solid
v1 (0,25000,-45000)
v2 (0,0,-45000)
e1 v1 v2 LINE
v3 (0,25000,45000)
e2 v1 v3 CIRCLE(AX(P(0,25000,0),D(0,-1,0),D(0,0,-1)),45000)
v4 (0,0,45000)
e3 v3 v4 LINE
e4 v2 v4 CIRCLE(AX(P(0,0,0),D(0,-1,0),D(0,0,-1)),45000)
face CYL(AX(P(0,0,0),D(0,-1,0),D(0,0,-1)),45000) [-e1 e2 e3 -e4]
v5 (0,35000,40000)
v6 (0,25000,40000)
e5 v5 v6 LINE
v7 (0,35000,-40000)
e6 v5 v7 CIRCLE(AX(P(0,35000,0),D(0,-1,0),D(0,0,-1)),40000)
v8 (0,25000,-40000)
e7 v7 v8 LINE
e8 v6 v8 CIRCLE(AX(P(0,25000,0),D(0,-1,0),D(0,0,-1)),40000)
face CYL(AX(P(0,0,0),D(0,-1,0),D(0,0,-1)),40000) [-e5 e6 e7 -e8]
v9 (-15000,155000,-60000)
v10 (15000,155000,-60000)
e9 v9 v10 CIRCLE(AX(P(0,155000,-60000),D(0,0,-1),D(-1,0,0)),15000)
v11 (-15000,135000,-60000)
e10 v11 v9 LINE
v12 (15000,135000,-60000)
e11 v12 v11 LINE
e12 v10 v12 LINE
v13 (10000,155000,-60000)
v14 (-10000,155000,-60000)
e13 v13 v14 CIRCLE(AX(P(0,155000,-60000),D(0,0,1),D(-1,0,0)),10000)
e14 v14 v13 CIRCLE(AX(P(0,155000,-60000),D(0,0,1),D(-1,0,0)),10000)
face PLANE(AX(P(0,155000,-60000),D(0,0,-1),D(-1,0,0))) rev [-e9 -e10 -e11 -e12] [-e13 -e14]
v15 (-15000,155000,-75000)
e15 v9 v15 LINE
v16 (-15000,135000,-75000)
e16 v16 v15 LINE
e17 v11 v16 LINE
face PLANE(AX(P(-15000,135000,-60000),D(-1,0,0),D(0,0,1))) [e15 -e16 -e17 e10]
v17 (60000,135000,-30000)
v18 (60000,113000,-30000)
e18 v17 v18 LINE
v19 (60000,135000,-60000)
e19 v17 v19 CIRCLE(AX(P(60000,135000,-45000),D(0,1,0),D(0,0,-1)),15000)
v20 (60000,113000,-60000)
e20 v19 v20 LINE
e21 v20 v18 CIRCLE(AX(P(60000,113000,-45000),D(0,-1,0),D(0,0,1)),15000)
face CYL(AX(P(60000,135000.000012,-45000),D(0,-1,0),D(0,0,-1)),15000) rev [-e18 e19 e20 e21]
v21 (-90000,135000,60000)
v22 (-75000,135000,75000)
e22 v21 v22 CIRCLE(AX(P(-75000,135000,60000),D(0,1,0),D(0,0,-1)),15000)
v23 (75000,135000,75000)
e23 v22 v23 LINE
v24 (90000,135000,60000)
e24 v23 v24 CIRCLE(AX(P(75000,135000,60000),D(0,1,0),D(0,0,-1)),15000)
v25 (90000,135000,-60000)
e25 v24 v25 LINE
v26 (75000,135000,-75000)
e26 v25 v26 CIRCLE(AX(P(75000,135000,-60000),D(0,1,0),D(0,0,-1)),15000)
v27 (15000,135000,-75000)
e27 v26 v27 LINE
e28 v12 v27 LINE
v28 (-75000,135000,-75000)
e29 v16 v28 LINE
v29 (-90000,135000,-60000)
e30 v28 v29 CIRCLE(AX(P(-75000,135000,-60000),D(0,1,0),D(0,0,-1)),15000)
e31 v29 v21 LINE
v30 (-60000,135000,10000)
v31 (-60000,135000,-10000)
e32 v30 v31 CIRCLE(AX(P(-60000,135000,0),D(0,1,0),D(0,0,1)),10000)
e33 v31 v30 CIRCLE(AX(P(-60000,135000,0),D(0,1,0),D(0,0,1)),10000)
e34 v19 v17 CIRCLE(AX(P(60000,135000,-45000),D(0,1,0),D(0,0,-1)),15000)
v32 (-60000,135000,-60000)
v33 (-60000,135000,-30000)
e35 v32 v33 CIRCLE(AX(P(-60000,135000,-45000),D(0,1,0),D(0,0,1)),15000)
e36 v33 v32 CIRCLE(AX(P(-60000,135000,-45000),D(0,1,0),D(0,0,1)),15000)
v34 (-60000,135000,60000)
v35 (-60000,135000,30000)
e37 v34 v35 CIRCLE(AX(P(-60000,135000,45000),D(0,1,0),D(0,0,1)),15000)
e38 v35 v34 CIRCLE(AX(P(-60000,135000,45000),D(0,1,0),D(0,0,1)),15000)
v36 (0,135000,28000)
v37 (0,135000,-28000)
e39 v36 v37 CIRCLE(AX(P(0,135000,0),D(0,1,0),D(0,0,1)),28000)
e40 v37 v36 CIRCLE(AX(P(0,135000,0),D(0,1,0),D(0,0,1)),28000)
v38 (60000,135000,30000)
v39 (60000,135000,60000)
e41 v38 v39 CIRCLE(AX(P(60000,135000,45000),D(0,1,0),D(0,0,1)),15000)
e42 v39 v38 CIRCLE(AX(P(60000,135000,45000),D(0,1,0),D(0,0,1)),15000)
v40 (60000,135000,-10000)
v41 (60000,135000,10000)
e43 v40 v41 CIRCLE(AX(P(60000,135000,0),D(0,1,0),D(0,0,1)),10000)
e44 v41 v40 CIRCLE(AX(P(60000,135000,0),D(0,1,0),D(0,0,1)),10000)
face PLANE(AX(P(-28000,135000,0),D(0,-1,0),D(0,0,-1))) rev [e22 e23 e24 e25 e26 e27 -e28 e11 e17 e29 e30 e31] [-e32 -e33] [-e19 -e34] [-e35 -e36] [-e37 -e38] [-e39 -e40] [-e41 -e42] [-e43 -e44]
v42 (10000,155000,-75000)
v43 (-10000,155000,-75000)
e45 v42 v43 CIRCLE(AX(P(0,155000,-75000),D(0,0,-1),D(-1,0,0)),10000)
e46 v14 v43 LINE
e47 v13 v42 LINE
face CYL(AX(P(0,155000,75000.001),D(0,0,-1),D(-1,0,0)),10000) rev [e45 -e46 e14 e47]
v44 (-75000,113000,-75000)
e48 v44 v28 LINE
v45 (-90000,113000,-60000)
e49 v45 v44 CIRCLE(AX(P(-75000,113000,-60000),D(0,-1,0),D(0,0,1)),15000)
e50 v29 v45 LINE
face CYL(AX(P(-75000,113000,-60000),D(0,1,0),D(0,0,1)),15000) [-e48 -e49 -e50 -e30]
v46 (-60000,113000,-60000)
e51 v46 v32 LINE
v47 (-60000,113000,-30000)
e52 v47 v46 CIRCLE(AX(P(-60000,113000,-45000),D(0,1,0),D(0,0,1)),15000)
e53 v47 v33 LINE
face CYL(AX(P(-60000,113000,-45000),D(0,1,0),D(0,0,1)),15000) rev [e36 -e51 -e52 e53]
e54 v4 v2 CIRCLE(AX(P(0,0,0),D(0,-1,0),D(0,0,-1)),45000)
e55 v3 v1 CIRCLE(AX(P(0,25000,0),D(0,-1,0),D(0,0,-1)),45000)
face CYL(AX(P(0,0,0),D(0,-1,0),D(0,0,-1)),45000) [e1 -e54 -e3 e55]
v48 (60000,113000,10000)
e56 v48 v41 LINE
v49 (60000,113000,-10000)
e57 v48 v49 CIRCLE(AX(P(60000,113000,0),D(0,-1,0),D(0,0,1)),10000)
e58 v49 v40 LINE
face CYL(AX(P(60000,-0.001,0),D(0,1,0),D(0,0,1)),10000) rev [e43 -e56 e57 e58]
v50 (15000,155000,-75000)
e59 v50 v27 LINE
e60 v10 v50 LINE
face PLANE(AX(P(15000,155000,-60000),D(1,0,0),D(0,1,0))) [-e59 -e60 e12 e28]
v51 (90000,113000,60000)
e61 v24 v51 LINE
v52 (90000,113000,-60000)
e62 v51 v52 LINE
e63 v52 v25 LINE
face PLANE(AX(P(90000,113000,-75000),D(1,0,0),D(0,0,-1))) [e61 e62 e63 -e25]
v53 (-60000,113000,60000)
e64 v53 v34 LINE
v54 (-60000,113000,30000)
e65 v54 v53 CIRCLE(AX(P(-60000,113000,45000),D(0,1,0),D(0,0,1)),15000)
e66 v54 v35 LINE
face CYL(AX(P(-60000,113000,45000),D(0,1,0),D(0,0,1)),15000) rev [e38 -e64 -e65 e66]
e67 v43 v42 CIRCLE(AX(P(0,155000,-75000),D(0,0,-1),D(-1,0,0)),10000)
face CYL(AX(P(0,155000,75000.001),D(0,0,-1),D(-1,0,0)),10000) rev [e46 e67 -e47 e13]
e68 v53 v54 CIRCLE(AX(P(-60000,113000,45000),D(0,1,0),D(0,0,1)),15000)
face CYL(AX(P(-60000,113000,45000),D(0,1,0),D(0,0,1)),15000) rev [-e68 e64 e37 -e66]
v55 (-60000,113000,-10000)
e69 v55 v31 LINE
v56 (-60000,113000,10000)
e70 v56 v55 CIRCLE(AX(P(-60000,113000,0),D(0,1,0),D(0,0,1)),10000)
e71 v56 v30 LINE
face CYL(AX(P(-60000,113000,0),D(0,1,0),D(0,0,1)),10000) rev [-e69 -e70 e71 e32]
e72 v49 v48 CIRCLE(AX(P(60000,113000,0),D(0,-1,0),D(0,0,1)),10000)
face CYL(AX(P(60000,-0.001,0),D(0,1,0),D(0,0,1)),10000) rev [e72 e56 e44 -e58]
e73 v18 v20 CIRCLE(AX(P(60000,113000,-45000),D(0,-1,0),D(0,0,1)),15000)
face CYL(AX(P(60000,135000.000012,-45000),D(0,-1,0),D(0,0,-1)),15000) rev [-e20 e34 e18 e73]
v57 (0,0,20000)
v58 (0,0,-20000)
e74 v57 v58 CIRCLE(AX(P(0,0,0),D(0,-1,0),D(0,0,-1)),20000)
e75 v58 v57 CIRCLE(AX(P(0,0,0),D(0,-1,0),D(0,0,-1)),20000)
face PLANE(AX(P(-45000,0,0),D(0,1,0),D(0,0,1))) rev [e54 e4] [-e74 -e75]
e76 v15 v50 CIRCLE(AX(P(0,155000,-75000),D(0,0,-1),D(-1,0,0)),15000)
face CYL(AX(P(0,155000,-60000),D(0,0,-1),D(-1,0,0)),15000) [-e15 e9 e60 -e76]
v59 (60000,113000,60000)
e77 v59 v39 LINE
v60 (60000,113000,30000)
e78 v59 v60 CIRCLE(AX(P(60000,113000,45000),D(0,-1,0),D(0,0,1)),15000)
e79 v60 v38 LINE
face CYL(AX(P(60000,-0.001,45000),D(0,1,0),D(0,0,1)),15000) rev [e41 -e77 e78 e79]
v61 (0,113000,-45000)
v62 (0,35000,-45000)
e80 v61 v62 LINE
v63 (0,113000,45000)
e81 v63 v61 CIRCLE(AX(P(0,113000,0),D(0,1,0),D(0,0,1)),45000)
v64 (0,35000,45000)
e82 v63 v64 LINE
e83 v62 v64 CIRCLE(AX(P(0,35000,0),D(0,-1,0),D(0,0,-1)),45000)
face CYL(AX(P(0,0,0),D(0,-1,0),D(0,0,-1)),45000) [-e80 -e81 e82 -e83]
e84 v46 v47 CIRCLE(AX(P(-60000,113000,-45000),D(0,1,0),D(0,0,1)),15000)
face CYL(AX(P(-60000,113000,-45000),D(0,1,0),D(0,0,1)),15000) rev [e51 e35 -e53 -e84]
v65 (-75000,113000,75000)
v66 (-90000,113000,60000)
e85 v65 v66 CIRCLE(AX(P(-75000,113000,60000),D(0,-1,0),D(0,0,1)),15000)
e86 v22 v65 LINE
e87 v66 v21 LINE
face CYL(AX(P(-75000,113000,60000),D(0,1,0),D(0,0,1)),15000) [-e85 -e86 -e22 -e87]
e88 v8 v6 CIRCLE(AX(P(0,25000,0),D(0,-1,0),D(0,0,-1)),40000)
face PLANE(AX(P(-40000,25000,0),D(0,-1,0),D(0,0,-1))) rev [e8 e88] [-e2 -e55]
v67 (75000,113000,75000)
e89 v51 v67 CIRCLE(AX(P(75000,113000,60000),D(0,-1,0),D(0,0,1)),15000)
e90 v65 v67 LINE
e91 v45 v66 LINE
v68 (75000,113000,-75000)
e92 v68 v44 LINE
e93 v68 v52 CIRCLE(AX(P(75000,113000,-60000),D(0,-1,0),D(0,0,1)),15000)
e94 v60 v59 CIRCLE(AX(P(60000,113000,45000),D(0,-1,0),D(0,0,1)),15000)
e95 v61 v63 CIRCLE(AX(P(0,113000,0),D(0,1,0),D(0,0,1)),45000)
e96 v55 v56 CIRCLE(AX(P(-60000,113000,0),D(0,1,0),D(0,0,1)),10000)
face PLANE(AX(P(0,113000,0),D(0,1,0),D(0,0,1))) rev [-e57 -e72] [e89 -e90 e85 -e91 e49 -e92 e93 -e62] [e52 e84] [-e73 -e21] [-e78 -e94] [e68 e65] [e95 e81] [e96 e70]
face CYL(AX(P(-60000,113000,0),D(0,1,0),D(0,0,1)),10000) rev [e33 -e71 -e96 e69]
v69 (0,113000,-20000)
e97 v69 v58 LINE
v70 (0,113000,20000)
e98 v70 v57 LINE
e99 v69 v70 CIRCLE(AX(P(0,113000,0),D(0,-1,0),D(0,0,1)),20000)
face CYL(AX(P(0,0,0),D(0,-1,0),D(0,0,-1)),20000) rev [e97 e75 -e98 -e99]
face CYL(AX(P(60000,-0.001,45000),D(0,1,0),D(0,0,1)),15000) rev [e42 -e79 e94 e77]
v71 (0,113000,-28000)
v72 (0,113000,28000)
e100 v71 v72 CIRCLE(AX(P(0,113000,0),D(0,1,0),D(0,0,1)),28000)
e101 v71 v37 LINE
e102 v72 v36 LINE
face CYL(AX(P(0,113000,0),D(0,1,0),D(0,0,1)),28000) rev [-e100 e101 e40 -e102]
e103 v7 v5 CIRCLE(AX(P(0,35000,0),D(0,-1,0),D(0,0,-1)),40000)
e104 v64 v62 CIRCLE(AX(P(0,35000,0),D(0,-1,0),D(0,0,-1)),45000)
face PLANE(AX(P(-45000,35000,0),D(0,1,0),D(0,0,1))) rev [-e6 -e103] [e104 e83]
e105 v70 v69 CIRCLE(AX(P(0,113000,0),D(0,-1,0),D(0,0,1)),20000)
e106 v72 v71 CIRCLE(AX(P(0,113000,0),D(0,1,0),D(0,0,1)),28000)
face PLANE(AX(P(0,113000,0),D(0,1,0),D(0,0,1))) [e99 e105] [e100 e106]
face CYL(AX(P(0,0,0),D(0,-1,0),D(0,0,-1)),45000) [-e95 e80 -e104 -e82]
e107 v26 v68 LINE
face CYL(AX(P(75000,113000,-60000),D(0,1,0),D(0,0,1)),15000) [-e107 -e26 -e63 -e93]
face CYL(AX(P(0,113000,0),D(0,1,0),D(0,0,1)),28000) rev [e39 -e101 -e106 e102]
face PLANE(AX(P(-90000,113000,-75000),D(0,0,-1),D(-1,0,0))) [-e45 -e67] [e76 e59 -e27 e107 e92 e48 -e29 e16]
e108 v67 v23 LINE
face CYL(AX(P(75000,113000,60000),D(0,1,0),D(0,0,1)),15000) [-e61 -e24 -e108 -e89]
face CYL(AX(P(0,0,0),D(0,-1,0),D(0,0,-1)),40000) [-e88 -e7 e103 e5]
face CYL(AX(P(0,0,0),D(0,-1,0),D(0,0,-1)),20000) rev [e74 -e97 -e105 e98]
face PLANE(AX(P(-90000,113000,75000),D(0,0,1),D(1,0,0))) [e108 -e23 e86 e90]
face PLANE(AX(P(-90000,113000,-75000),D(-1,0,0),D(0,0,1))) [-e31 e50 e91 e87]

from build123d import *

# Parameters (mm, degrees)
FLANGE_PROFILE_180X150_W         = 180000
FLANGE_PROFILE_180X150_H         = 150000
SQUARE_FLANGE_DEPTH              = 22000
CENTRE_RECESS_SKETCH_R           = 28000
CENTRE_RECESS_DEPTH              = 22000
FLANGE_CORNER_FILLET_R15_A_R     = 15000
FLANGE_CORNER_FILLET_R15_B_R     = 15000
FLANGE_CORNER_FILLET_R15_C_R     = 15000
FLANGE_CORNER_FILLET_R15_D_R     = 15000
BOLT_HOLE_30_A_SKETCH_R          = 15000
BOLT_HOLE_30_A_DEPTH             = 22000
PIN_HOLE_20_A_SKETCH_R           = 10000
PIN_HOLE_20_A_DEPTH              = 22000
BOLT_HOLE_30_B_SKETCH_R          = 15000
BOLT_HOLE_30_B_DEPTH             = 22000
BOLT_HOLE_30_C_REACH             = 178747.629
BOLT_HOLE_30_C_SKETCH_R          = 15000
BOLT_HOLE_30_C_DIRECTION_2_DEPTH = 178746.629317195
PIN_HOLE_20_B_REACH              = 178747.629
PIN_HOLE_20_B_SKETCH_R           = 10000
BOLT_HOLE_30_D_REACH             = 178747.629
BOLT_HOLE_30_D_SKETCH_R          = 15000
LIFTING_LUG_DEPTH                = 15000
LIFTING_EYE_HOLE_REACH           = 243928.218
LIFTING_EYE_HOLE_SKETCH_R        = 10000


with BuildPart() as part:
    # Plug Body Profile → Plug Body (revolve)
    with BuildSketch(Plane.XY, mode=Mode.PRIVATE) as plug_body_sk:
        Polygon((-20000, 0), (-20000, 121000), (-28000, 121000), (-28000, 135000), (-53000, 135000), (-53000, 115000), (-45000, 115000), (-45000, 35000), (-40000, 35000), (-40000, 25000), (-45000, 25000), (-45000, 0), align=None)
    revolve(plug_body_sk.sketch.rotate(Axis((0, 0, 0), (0, 1, 0)), 270), axis=Axis((0, 0, 0), (0, 1, 0)))

    # Flange Profile 180x150 → Square Flange (add)
    with BuildSketch(Plane(origin=(0, 135000, 0), x_dir=(1, 0, 0), z_dir=(0, 1, 0))):
        Rectangle(FLANGE_PROFILE_180X150_W, FLANGE_PROFILE_180X150_H)
    extrude(amount=-SQUARE_FLANGE_DEPTH)

    # Centre Recess Sketch → Centre Recess (cut)
    with BuildSketch(Plane(origin=(0, 135000, 0), x_dir=(1, 0, 0), z_dir=(0, 1, 0))):
        with Locations(Location((0, 0, 0), (0, 0, 270))):
            Circle(CENTRE_RECESS_SKETCH_R)
    extrude(amount=-CENTRE_RECESS_DEPTH, mode=Mode.SUBTRACT)

    # Flange Corner Fillet R15 A
    flange_corner_fillet_r15_a_edges = [part.edges().sort_by_distance(p)[0] for p in [
        (90000, 124000, 75000),
    ]]
    fillet(flange_corner_fillet_r15_a_edges, radius=FLANGE_CORNER_FILLET_R15_A_R)

    # Flange Corner Fillet R15 B
    flange_corner_fillet_r15_b_edges = [part.edges().sort_by_distance(p)[0] for p in [
        (-90000, 124000, 75000),
    ]]
    fillet(flange_corner_fillet_r15_b_edges, radius=FLANGE_CORNER_FILLET_R15_B_R)

    # Flange Corner Fillet R15 C
    flange_corner_fillet_r15_c_edges = [part.edges().sort_by_distance(p)[0] for p in [
        (-90000, 124000, -75000),
    ]]
    fillet(flange_corner_fillet_r15_c_edges, radius=FLANGE_CORNER_FILLET_R15_C_R)

    # Flange Corner Fillet R15 D
    flange_corner_fillet_r15_d_edges = [part.edges().sort_by_distance(p)[0] for p in [
        (90000, 124000, -75000),
    ]]
    fillet(flange_corner_fillet_r15_d_edges, radius=FLANGE_CORNER_FILLET_R15_D_R)

    # Bolt Hole Ø30 A Sketch → Bolt Hole Ø30 A (cut)
    with BuildSketch(Plane(origin=(0, 135000, 0), x_dir=(1, 0, 0), z_dir=(0, 1, 0))):
        with Locations(Location((-60000, -45000, 0), (0, 0, 270))):
            Circle(BOLT_HOLE_30_A_SKETCH_R)
    extrude(amount=-BOLT_HOLE_30_A_DEPTH, mode=Mode.SUBTRACT)

    # Pin Hole Ø20 A Sketch → Pin Hole Ø20 A (cut)
    with BuildSketch(Plane(origin=(0, 135000, 0), x_dir=(1, 0, 0), z_dir=(0, 1, 0))):
        with Locations(Location((-60000, 0, 0), (0, 0, 270))):
            Circle(PIN_HOLE_20_A_SKETCH_R)
    extrude(amount=-PIN_HOLE_20_A_DEPTH, mode=Mode.SUBTRACT)

    # Bolt Hole Ø30 B Sketch → Bolt Hole Ø30 B (cut)
    with BuildSketch(Plane(origin=(0, 135000, 0), x_dir=(1, 0, 0), z_dir=(0, 1, 0))):
        with Locations(Location((-60000, 45000, 0), (0, 0, 270))):
            Circle(BOLT_HOLE_30_B_SKETCH_R)
    extrude(amount=-BOLT_HOLE_30_B_DEPTH, mode=Mode.SUBTRACT)

    # Bolt Hole Ø30 C Sketch → Bolt Hole Ø30 C (cut, up to next)
    with BuildSketch(Plane(origin=(0, 135000, 0), x_dir=(1, 0, 0), z_dir=(0, 1, 0)), mode=Mode.PRIVATE) as bolt_hole_30_c_sk1:
        with Locations(Location((60000, 45000, 0), (0, 0, 90))):
            Circle(BOLT_HOLE_30_C_SKETCH_R)
    bolt_hole_30_c_tool1 = extrude(bolt_hole_30_c_sk1.sketch, amount=-BOLT_HOLE_30_C_REACH, mode=Mode.PRIVATE) & part.part
    add(bolt_hole_30_c_tool1.solids().sort_by_distance((60000, 135000, -45000))[0], mode=Mode.SUBTRACT)

    # Bolt Hole Ø30 C Sketch → Bolt Hole Ø30 C direction 2 (cut)
    with BuildSketch(Plane(origin=(0, 135000, 0), x_dir=(1, 0, 0), z_dir=(0, 1, 0))):
        with Locations(Location((60000, 45000, 0), (0, 0, 90))):
            Circle(BOLT_HOLE_30_C_SKETCH_R)
    extrude(amount=BOLT_HOLE_30_C_DIRECTION_2_DEPTH, mode=Mode.SUBTRACT)

    # Pin Hole Ø20 B Sketch → Pin Hole Ø20 B (cut, up to next)
    with BuildSketch(Plane(origin=(0, 135000, 0), x_dir=(1, 0, 0), z_dir=(0, 1, 0)), mode=Mode.PRIVATE) as pin_hole_20_b_sk1:
        with Locations(Location((60000, 0, 0), (0, 0, 270))):
            Circle(PIN_HOLE_20_B_SKETCH_R)
    pin_hole_20_b_tool1 = extrude(pin_hole_20_b_sk1.sketch, amount=-PIN_HOLE_20_B_REACH, mode=Mode.PRIVATE) & part.part
    add(pin_hole_20_b_tool1.solids().sort_by_distance((60000, 135000, 0))[0], mode=Mode.SUBTRACT)

    # Bolt Hole Ø30 D Sketch → Bolt Hole Ø30 D (cut, up to next)
    with BuildSketch(Plane(origin=(0, 135000, 0), x_dir=(1, 0, 0), z_dir=(0, 1, 0)), mode=Mode.PRIVATE) as bolt_hole_30_d_sk1:
        with Locations(Location((60000, -45000, 0), (0, 0, 270))):
            Circle(BOLT_HOLE_30_D_SKETCH_R)
    bolt_hole_30_d_tool1 = extrude(bolt_hole_30_d_sk1.sketch, amount=-BOLT_HOLE_30_D_REACH, mode=Mode.PRIVATE) & part.part
    add(bolt_hole_30_d_tool1.solids().sort_by_distance((60000, 135000, 45000))[0], mode=Mode.SUBTRACT)

    # Lifting Lug Profile → Lifting Lug (add)
    with BuildSketch(Plane(origin=(0, 0, -75000), x_dir=(-1, 0, 0), z_dir=(0, 0, -1))):
        with BuildLine():
            Line((0, 135000), (15000, 135000))
            Line((15000, 135000), (15000, 155000))
            ThreePointArc((15000, 155000), (0, 170000), (-15000, 155000))
            Line((-15000, 155000), (-15000, 135000))
            Line((-15000, 135000), (0, 135000))
        make_face()
    extrude(amount=-LIFTING_LUG_DEPTH)

    # Lifting Eye Hole Sketch → Lifting Eye Hole (cut, up to next)
    with BuildSketch(Plane(origin=(0, 0, -75000), x_dir=(-1, 0, 0), z_dir=(0, 0, -1)), mode=Mode.PRIVATE) as lifting_eye_hole_sk1:
        with Locations((0, 155000)):
            Circle(LIFTING_EYE_HOLE_SKETCH_R)
    lifting_eye_hole_tool1 = extrude(lifting_eye_hole_sk1.sketch, amount=-LIFTING_EYE_HOLE_REACH, mode=Mode.PRIVATE) & part.part
    add(lifting_eye_hole_tool1.solids().sort_by_distance((0, 155000, -75000))[0], mode=Mode.SUBTRACT)


solid = part.part
